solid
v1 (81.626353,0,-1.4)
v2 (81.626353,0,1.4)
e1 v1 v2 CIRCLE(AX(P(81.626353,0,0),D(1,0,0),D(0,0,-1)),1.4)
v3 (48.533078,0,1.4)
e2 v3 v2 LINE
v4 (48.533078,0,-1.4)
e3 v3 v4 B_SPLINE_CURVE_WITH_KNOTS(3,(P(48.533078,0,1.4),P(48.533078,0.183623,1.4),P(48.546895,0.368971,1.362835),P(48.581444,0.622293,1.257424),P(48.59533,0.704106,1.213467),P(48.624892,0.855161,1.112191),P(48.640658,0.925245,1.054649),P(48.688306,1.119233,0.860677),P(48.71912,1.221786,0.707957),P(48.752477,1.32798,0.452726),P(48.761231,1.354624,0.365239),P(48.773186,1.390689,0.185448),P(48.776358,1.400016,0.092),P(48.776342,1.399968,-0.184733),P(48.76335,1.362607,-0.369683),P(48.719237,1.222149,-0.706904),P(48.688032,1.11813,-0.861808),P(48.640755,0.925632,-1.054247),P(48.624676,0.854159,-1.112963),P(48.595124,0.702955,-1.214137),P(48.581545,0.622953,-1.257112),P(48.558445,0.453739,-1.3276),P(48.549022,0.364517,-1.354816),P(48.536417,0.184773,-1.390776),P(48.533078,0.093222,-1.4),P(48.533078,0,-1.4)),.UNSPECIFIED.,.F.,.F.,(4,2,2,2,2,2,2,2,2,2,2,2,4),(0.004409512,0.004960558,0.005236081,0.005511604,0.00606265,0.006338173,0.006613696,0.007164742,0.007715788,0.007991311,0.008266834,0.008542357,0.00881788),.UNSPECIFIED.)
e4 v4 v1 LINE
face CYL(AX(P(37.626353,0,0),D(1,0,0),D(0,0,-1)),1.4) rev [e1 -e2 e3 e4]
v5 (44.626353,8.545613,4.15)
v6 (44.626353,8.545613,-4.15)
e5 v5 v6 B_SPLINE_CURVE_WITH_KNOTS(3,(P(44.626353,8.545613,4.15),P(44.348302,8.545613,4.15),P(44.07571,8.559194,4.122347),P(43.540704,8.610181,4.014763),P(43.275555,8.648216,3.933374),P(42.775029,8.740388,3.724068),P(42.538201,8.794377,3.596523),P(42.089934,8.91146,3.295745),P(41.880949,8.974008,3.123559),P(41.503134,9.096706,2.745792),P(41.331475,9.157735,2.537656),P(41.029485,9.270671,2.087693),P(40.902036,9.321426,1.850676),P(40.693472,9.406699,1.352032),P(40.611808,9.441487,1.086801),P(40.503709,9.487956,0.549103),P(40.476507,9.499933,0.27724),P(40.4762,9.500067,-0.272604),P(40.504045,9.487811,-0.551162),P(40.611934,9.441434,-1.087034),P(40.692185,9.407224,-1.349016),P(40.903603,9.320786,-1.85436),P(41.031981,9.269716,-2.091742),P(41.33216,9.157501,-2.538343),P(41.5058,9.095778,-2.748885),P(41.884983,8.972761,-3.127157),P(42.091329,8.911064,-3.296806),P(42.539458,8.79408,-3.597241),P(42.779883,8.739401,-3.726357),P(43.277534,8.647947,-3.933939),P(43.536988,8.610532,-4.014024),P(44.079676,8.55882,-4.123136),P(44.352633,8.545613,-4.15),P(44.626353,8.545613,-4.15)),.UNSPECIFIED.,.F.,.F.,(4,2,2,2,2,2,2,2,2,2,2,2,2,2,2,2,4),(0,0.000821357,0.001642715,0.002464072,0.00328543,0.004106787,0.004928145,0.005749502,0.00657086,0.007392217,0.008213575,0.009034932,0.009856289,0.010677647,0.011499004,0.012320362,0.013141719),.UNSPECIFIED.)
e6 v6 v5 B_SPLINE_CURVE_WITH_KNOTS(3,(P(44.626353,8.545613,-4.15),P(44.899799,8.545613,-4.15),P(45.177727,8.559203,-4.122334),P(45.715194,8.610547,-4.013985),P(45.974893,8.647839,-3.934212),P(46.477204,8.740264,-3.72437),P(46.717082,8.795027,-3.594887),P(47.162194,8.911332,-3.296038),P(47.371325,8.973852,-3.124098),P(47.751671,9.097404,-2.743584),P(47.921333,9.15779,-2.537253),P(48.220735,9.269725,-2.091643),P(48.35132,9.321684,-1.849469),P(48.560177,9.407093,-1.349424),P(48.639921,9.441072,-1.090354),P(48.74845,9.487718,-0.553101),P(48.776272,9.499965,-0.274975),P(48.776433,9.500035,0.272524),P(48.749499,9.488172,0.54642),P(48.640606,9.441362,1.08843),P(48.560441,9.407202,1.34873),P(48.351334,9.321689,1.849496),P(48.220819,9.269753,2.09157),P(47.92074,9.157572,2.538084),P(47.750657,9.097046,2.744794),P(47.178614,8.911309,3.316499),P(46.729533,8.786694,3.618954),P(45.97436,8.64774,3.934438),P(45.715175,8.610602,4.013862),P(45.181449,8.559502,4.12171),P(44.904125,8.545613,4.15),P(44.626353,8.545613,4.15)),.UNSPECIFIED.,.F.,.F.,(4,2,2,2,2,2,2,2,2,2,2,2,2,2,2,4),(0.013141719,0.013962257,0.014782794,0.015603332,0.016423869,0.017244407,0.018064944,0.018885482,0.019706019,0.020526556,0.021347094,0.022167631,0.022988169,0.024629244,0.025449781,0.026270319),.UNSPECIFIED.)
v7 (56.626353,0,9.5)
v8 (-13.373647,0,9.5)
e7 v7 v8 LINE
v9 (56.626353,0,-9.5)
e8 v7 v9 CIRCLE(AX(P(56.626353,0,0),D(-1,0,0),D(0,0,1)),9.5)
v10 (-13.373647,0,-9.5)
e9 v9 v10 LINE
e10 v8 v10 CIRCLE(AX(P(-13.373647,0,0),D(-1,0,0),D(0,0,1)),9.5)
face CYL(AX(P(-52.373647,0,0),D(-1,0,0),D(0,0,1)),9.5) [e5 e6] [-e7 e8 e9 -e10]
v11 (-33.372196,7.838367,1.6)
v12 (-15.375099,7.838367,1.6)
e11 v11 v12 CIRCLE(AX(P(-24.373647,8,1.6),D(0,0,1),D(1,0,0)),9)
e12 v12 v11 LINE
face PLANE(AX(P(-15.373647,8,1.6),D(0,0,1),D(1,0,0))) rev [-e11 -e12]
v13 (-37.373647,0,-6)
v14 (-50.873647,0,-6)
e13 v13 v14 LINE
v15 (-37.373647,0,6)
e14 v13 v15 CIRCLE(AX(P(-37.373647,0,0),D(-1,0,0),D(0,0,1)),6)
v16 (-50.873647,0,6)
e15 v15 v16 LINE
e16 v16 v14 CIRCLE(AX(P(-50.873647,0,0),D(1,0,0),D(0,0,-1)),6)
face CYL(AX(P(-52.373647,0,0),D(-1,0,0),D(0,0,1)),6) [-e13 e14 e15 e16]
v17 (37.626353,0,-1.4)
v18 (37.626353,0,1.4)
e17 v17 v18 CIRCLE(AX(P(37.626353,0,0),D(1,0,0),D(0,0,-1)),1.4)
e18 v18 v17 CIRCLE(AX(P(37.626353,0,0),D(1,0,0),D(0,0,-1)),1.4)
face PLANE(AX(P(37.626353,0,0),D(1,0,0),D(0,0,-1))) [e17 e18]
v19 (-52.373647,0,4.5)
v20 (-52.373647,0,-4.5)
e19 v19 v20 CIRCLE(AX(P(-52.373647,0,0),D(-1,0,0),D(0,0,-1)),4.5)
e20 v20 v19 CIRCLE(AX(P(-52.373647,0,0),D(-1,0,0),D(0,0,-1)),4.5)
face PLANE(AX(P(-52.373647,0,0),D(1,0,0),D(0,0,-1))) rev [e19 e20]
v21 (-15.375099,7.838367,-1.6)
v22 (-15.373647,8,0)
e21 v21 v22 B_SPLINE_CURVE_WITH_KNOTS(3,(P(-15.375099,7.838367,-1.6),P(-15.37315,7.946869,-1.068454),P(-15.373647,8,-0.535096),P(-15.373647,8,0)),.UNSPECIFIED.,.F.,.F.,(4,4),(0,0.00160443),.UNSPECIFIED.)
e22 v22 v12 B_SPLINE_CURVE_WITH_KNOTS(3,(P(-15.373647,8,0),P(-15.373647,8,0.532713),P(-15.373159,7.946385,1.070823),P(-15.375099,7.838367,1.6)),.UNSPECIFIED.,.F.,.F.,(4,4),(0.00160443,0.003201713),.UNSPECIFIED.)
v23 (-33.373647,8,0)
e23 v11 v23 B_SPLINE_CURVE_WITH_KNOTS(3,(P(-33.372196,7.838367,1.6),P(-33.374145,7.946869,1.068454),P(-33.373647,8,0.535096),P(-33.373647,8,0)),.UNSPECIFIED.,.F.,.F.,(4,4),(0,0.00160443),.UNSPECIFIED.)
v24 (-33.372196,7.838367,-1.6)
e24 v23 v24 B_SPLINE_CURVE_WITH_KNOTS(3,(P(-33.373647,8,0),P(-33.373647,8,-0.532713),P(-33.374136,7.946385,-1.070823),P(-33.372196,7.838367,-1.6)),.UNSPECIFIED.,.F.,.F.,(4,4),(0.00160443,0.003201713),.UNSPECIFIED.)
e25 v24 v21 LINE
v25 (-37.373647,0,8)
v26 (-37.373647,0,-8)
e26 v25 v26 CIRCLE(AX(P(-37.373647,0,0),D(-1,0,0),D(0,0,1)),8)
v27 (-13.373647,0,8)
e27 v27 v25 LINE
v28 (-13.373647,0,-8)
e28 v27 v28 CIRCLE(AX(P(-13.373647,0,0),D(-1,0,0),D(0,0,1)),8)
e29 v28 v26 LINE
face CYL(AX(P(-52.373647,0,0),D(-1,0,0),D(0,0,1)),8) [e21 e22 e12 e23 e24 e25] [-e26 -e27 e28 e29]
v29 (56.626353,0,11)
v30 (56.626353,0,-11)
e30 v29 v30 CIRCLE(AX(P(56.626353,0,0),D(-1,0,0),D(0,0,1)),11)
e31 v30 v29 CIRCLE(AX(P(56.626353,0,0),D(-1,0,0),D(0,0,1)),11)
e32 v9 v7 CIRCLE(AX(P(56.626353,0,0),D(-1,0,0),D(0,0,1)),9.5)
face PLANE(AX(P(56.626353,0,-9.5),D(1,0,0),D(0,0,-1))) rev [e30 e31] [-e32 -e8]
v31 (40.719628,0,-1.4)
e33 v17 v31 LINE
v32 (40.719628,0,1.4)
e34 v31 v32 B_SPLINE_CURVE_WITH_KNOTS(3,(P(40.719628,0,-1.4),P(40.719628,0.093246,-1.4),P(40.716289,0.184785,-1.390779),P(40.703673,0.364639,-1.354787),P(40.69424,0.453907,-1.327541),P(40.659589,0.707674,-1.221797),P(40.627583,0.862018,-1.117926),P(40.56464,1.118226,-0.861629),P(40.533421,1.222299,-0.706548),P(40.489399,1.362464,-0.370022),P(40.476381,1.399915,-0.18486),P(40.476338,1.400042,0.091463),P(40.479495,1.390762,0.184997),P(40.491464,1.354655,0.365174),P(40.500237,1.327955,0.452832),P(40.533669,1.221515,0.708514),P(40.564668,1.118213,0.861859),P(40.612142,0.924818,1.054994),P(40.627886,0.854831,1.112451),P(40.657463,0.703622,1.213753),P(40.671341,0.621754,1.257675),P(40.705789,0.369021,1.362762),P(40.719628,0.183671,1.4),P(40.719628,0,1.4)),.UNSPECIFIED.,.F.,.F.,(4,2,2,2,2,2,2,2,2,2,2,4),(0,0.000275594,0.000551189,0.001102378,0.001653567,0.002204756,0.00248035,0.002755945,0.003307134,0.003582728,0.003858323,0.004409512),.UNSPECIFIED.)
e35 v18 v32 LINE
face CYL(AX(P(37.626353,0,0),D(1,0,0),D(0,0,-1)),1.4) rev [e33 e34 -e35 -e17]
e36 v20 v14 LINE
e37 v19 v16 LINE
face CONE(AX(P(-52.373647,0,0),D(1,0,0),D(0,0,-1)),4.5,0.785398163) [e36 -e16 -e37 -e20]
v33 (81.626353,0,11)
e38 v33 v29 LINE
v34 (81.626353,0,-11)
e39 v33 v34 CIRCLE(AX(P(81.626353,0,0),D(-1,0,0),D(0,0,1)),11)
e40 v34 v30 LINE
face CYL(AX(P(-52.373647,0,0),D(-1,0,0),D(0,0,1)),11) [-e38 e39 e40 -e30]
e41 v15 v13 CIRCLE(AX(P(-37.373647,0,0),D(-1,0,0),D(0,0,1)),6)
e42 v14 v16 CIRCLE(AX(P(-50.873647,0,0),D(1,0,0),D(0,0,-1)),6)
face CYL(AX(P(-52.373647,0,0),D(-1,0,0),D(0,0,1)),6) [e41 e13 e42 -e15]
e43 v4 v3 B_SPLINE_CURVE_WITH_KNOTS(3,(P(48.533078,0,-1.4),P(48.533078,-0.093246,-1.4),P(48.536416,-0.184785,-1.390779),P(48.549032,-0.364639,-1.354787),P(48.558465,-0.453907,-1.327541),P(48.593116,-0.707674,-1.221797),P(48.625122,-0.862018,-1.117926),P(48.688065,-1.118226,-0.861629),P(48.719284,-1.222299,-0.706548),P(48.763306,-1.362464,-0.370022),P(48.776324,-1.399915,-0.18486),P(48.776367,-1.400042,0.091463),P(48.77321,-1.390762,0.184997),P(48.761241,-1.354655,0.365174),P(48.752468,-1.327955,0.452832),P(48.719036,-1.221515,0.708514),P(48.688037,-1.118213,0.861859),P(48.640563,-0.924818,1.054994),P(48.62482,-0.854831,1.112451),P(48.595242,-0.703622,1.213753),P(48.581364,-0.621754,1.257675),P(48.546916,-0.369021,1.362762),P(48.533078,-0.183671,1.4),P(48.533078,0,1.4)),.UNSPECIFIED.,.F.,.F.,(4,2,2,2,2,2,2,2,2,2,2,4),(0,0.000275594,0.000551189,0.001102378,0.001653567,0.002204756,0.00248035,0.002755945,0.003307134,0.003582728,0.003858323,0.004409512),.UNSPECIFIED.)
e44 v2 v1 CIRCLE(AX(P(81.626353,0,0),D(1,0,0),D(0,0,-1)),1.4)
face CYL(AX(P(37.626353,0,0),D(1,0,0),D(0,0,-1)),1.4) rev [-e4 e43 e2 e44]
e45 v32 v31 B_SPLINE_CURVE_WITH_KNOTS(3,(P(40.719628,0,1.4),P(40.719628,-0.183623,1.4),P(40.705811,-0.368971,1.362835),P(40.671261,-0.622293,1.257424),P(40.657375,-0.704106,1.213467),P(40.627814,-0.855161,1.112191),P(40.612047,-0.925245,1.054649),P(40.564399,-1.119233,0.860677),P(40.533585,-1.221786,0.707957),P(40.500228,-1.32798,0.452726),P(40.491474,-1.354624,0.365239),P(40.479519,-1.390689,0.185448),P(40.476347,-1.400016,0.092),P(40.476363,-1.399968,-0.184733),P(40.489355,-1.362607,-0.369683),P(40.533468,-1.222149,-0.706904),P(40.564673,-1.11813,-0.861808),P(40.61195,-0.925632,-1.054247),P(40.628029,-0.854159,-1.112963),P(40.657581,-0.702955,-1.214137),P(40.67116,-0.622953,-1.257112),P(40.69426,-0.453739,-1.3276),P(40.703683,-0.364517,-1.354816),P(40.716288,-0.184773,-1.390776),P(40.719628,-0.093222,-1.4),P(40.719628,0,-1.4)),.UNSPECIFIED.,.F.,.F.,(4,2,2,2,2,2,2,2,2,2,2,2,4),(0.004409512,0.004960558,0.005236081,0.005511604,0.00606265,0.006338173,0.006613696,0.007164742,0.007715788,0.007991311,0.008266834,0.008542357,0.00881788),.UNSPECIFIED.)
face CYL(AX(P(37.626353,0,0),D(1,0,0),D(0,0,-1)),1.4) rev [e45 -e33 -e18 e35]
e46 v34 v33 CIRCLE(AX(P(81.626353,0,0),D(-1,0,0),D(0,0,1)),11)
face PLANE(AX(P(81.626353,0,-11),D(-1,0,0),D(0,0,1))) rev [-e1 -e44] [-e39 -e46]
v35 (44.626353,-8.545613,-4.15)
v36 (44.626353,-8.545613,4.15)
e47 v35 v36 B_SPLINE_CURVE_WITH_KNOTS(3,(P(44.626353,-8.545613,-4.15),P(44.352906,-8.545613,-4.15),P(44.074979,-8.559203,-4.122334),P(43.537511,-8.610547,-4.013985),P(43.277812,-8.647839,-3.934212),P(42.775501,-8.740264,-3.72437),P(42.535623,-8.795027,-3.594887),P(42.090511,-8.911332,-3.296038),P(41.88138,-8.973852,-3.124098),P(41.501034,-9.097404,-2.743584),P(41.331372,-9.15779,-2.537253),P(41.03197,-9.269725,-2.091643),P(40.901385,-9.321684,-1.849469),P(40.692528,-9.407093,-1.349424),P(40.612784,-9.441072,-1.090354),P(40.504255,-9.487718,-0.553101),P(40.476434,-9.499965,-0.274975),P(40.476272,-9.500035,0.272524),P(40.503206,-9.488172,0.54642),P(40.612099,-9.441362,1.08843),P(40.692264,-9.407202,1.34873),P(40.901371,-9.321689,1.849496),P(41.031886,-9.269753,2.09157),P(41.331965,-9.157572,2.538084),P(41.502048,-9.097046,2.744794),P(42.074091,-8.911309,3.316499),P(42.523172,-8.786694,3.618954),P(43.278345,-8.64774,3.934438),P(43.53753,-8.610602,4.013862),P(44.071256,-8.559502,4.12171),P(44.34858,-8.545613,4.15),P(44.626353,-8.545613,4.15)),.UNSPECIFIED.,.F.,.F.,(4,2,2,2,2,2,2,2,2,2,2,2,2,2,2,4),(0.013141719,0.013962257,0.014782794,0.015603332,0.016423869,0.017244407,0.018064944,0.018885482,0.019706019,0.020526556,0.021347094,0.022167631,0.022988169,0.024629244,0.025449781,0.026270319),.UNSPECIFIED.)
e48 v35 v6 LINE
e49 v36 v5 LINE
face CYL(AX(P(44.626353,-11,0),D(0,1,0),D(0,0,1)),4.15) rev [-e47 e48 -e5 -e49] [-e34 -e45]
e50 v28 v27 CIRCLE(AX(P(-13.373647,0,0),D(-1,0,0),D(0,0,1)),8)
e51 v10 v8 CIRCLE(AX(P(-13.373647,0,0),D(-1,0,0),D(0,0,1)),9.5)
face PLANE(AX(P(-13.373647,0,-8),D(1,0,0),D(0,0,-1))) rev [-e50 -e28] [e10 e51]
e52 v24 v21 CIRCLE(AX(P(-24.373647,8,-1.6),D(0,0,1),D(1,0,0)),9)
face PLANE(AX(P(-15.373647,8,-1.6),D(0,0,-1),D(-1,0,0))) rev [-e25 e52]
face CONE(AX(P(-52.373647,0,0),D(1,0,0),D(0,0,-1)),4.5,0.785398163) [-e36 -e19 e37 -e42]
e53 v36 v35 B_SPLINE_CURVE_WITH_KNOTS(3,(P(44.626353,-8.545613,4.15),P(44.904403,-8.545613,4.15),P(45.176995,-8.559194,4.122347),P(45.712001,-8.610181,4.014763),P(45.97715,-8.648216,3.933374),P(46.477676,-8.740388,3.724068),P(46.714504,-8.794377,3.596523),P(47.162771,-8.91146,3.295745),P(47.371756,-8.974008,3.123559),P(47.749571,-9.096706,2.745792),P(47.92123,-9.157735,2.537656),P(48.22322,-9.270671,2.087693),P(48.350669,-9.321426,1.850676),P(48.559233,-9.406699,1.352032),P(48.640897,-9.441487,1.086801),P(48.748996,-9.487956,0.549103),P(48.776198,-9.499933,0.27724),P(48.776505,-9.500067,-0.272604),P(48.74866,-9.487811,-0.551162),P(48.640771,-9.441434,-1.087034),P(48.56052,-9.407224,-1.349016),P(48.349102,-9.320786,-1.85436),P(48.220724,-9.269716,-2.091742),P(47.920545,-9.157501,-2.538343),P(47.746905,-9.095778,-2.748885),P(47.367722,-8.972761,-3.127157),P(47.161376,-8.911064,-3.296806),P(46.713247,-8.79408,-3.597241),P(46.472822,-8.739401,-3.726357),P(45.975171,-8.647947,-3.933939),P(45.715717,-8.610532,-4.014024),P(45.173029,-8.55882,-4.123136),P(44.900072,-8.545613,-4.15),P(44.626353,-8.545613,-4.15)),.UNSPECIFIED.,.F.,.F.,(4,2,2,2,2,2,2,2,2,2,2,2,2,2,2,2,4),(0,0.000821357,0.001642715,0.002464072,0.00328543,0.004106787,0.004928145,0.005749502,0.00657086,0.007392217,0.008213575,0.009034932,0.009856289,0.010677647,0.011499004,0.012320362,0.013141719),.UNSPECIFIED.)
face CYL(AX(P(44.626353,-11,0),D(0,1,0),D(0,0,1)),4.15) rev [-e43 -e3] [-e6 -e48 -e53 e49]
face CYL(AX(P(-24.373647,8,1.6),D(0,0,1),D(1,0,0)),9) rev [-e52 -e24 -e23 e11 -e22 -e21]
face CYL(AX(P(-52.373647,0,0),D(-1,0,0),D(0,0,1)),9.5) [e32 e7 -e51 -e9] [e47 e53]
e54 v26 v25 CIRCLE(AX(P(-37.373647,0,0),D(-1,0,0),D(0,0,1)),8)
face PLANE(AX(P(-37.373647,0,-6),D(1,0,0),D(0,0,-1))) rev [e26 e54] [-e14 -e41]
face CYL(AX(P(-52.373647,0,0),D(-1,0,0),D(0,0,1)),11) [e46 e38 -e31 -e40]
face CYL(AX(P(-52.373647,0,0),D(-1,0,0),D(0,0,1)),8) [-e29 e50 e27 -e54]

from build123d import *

# Parameters (mm, degrees)
SKETCH2_R               = 1.4
CUT_EXTRUDE1_DEPTH      = 44
CUT_EXTRUDE2_DEPTH      = 84.095495831
CUT_EXTRUDE2_DEPTH_BACK = 84.095495831
SKETCH3_R               = 4.15
SKETCH5_W               = 9
SKETCH5_H               = 3.2
CHAMFER1_SIZE           = 1.5


with BuildPart() as part:
    # Sketch1 → Revolve1 (revolve)
    with BuildSketch(Plane(origin=(0, 0, 0), x_dir=(1, 0, 0), z_dir=(0, 1, 0)), mode=Mode.PRIVATE) as revolve1_sk:
        Polygon((-52.373647469, 0), (-52.373647469, 6), (-37.373647469, 6), (-37.373647469, 8), (-13.373647469, 8), (-13.373647469, 9.5), (56.626352531, 9.5), (56.626352531, 11), (81.626352531, 11), (81.626352531, 0), align=None)
    revolve(revolve1_sk.sketch.rotate(Axis((-52.373647469, 0, 0), (1, 0, 0)), 180), axis=Axis((-52.373647469, 0, 0), (1, 0, 0)))

    # Sketch2 → Cut-Extrude1 (cut)
    with BuildSketch(Plane(origin=(81.626352531, 0, 0), x_dir=(0, 0, -1), z_dir=(1, 0, 0))):
        Circle(SKETCH2_R)
    extrude(amount=-CUT_EXTRUDE1_DEPTH, mode=Mode.SUBTRACT)

    # Sketch3 → Cut-Extrude2 (cut, two sides: drawn at the far end of the back side and taken through both)
    with BuildSketch(Plane(origin=(0, 0, 0), x_dir=(1, 0, 0), z_dir=(0, 1, 0)).offset(-CUT_EXTRUDE2_DEPTH_BACK)):
        with Locations(Location((44.626352531, 0, 0), (0, 0, 270))):
            Circle(SKETCH3_R)
    extrude(amount=CUT_EXTRUDE2_DEPTH + CUT_EXTRUDE2_DEPTH_BACK, mode=Mode.SUBTRACT)

    # Sketch5 → Cut-Revolve3 (revolve, cut)
    with BuildSketch(Plane(origin=(0, 8, 0), x_dir=(-1, 0, 0), z_dir=(0, 1, 0))):
        with Locations((19.873647469, 0)):
            Rectangle(SKETCH5_W, SKETCH5_H)
    revolve(axis=Axis((-24.373647469, 8, 1.6), (0, 0, -1)), mode=Mode.SUBTRACT)

    # Chamfer1
    chamfer1_edges = [part.edges().sort_by_distance(p)[0] for p in [
        (-52.373647469, 0, -6),
    ]]
    chamfer(chamfer1_edges, length=CHAMFER1_SIZE)


solid = part.part
